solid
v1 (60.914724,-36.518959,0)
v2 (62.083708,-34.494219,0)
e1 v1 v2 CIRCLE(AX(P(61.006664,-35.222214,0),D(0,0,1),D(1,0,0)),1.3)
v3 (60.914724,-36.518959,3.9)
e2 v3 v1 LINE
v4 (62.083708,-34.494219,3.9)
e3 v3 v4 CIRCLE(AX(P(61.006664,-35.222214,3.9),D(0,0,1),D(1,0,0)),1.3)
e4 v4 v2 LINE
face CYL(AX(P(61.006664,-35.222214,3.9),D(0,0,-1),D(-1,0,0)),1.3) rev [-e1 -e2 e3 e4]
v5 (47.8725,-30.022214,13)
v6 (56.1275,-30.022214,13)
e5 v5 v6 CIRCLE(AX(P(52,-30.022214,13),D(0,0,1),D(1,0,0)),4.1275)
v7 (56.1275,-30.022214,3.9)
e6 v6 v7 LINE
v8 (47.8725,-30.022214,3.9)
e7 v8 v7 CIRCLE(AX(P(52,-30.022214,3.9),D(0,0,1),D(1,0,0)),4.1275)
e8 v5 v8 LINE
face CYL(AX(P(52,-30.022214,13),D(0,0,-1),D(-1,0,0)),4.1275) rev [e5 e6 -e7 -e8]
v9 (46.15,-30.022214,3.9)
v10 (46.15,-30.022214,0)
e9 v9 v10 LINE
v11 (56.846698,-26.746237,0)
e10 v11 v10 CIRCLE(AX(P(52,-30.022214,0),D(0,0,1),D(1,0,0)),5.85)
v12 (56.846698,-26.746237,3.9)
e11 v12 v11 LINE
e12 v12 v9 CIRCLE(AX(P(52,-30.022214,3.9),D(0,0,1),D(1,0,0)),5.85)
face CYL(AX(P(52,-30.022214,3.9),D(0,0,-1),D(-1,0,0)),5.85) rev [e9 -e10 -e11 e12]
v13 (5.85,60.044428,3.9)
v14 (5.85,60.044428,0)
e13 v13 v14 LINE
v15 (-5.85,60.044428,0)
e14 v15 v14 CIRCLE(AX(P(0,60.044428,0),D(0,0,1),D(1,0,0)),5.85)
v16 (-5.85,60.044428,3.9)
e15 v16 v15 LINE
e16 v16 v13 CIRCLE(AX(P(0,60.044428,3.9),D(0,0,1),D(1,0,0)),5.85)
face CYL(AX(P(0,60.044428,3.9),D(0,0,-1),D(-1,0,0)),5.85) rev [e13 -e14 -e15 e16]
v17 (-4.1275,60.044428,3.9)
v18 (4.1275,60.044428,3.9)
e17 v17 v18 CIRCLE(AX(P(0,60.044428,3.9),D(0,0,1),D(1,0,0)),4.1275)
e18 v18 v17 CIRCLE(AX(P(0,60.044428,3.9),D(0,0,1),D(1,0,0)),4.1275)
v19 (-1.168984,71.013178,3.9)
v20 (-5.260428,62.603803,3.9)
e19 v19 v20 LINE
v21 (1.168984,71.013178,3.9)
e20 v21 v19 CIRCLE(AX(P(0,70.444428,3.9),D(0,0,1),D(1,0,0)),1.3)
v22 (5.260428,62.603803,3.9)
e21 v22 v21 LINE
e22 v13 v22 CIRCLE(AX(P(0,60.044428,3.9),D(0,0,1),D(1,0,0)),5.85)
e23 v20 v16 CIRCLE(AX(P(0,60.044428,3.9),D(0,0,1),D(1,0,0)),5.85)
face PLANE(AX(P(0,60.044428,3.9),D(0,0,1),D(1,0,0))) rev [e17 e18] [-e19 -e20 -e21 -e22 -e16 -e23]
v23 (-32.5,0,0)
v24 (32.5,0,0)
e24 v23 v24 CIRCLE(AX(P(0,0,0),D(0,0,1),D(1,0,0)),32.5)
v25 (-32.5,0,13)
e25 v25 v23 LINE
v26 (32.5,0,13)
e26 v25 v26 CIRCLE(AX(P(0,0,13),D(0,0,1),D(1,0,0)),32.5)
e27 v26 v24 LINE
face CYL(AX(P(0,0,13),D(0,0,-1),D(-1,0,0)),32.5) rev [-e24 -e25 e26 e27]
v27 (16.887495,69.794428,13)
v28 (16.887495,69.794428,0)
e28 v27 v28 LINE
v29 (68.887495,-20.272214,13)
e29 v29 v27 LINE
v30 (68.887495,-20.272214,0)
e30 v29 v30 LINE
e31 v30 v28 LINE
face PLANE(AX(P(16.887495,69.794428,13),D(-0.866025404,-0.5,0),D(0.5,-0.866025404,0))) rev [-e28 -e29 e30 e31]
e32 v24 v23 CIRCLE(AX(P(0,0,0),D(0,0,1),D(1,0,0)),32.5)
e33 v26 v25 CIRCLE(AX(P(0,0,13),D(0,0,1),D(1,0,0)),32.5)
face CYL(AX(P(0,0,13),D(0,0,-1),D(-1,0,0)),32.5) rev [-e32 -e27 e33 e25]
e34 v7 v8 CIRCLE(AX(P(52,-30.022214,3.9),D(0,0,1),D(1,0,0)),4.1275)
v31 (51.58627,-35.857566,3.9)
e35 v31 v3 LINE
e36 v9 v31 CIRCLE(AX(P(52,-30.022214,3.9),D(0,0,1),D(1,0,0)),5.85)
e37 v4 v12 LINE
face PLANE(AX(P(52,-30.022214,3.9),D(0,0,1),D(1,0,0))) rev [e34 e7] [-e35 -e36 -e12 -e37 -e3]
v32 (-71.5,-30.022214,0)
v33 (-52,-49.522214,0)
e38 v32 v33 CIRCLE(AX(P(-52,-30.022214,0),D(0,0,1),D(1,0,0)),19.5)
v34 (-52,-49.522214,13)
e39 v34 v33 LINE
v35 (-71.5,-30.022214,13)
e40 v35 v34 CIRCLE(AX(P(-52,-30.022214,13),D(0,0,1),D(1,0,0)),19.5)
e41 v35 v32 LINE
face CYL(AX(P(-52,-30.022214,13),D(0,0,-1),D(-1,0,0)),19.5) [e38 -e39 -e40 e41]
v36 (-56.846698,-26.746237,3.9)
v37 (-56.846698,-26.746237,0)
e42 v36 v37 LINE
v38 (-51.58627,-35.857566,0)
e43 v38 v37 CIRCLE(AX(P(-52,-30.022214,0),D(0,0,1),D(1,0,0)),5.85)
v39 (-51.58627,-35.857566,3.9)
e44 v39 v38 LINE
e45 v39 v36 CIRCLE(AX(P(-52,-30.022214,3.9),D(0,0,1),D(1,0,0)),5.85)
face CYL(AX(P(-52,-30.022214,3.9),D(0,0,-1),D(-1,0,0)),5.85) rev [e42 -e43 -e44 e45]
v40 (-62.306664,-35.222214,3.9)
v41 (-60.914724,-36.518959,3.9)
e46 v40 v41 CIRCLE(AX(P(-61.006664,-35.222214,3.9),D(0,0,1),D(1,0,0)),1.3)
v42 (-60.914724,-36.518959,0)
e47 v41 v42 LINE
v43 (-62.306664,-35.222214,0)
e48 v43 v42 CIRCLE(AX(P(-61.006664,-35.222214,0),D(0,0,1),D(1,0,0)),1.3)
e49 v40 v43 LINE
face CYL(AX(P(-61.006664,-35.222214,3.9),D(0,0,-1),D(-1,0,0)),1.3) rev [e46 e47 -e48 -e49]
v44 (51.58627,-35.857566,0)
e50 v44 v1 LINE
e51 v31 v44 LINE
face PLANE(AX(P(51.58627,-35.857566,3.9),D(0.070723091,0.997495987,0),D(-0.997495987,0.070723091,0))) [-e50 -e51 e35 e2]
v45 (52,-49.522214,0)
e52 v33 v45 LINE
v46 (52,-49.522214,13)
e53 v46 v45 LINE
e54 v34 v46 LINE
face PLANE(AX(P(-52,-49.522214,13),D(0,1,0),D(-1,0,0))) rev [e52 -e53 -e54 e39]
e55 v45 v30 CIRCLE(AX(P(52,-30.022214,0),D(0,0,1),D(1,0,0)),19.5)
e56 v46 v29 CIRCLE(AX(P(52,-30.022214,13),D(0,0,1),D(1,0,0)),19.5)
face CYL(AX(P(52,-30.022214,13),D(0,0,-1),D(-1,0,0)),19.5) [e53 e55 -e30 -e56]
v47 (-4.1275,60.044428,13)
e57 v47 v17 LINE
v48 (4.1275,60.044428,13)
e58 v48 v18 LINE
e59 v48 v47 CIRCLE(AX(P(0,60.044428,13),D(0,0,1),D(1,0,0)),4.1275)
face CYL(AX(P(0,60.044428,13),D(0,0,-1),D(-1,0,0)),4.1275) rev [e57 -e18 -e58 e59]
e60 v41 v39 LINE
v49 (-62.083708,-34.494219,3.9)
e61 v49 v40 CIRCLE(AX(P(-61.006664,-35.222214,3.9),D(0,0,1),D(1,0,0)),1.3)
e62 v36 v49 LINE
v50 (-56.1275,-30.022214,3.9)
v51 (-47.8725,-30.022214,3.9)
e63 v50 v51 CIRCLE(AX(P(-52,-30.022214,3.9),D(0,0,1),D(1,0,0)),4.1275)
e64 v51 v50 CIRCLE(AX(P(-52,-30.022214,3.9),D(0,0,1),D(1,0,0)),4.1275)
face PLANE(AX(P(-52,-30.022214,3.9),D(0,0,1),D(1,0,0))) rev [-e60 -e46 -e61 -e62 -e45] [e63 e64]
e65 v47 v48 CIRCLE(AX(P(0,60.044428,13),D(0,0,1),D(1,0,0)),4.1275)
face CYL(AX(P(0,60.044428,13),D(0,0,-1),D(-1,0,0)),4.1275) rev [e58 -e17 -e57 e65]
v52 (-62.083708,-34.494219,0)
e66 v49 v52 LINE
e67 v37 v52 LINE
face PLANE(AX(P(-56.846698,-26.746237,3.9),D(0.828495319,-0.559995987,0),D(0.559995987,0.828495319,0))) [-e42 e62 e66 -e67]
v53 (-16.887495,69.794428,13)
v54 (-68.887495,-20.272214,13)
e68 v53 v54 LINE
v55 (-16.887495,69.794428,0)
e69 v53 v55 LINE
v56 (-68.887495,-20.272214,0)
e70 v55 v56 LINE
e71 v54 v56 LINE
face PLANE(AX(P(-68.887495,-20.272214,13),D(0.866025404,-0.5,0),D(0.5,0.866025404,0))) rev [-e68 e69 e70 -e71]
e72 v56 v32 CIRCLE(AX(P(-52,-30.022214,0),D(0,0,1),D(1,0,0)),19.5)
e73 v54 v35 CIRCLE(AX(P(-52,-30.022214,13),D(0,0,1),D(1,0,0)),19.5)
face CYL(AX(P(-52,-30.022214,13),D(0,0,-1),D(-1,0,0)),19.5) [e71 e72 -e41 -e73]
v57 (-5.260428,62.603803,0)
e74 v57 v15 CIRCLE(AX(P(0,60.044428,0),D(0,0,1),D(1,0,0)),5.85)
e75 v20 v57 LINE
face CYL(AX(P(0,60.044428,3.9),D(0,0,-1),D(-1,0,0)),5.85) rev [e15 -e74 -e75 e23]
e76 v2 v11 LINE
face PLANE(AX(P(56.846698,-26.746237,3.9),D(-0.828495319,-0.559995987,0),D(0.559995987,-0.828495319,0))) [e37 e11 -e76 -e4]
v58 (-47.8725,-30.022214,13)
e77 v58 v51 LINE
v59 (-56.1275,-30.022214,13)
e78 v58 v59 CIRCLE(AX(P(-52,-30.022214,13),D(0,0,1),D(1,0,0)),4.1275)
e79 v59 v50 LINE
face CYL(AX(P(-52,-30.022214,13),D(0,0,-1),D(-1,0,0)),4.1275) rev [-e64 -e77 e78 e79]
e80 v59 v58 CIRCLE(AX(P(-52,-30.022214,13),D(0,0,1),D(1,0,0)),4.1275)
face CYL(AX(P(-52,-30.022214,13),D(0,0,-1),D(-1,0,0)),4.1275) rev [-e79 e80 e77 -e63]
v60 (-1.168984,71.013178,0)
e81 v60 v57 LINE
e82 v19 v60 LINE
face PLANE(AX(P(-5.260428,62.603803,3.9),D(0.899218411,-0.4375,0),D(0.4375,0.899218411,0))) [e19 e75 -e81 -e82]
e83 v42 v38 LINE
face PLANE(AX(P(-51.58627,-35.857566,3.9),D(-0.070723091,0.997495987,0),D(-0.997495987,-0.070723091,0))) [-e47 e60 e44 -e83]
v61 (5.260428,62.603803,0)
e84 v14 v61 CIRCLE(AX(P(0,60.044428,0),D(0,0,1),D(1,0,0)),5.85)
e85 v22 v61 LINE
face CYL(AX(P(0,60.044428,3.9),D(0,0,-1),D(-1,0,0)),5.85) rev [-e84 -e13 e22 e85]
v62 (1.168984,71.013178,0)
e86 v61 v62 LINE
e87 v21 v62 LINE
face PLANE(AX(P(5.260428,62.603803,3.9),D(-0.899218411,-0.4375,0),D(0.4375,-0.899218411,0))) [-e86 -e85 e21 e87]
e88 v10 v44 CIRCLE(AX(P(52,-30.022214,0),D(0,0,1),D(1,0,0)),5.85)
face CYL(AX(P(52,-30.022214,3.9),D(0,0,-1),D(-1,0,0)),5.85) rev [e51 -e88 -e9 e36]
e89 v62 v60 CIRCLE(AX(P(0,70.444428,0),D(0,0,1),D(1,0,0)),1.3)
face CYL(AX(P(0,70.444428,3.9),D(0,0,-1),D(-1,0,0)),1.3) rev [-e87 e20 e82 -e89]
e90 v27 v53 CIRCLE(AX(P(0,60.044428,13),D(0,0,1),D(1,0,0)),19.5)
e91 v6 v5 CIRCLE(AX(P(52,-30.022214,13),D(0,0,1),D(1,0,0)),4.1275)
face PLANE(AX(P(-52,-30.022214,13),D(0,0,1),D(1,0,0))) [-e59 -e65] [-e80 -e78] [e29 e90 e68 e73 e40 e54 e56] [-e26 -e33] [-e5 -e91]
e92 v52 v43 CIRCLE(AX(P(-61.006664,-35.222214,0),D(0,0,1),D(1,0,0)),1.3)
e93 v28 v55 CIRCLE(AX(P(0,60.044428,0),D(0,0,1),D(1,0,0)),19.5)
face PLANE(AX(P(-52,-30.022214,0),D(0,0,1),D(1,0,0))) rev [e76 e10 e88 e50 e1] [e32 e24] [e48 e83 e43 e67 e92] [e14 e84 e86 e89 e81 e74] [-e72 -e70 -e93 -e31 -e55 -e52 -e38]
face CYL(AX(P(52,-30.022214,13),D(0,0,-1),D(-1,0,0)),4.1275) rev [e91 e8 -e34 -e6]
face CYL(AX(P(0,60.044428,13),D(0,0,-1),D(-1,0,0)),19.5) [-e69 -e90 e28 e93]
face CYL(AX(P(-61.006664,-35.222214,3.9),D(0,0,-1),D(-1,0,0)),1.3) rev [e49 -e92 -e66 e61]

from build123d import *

# Parameters (mm, degrees)
SKETCH1_R           = 3.175
SKETCH1_R_2         = 25
BOSS_EXTRUDE1_DEPTH = 10
SKETCH2_R           = 3.175
CUT_EXTRUDE1_DEPTH  = 3
SCALE_RATIO_1_SCALE = 1.3


with BuildPart() as part:
    # Sketch1 → Boss-Extrude1 (new body)
    with BuildSketch(Plane.XY):
        with BuildLine():
            Line((-52.990381057, -15.594010768), (-12.990381057, 53.688021535))
            ThreePointArc((-12.990381057, 53.688021535), (0, 61.188021535), (12.990381057, 53.688021535))
            Line((12.990381057, 53.688021535), (52.990381057, -15.594010768))
            ThreePointArc((52.990381057, -15.594010768), (52.990381057, -30.594010768), (40, -38.094010768))
            Line((40, -38.094010768), (-40, -38.094010768))
            ThreePointArc((-40, -38.094010768), (-52.990381057, -30.594010768), (-52.990381057, -15.594010768))
        make_face()
        with Locations((-40, -23.094010768)):
            Circle(SKETCH1_R, mode=Mode.SUBTRACT)
        with Locations((40, -23.094010768)):
            Circle(SKETCH1_R, mode=Mode.SUBTRACT)
        with Locations((0, 46.188021535)):
            Circle(SKETCH1_R, mode=Mode.SUBTRACT)
        Circle(SKETCH1_R_2, mode=Mode.SUBTRACT)
    extrude(amount=BOSS_EXTRUDE1_DEPTH)

    # Sketch2 → Cut-Extrude1 (cut)
    # profile 1 of 3: a face of its own
    with BuildSketch(Plane.XY):
        with BuildLine():
            Line((-39.68174609, -27.58274271), (-46.857480139, -28.091506755))
            ThreePointArc((-46.857480139, -28.091506755), (-47.794228634, -27.594010768), (-47.75669855, -26.53401478))
            Line((-47.75669855, -26.53401478), (-43.728228938, -20.574028825))
            ThreePointArc((-43.728228938, -20.574028825), (-36.102885683, -20.844010768), (-39.68174609, -27.58274271))
        make_face()
        with Locations((-40, -23.094010768)):
            Circle(SKETCH2_R, mode=Mode.SUBTRACT)
    # profile 2 of 3: a face of its own
    with BuildSketch(Plane.XY):
        with BuildLine():
            Line((-4.046482848, 48.156771535), (-0.899218411, 54.625521535))
            ThreePointArc((-0.899218411, 54.625521535), (0, 55.188021535), (0.899218411, 54.625521535))
            Line((0.899218411, 54.625521535), (4.046482848, 48.156771535))
            ThreePointArc((4.046482848, 48.156771535), (0, 41.688021535), (-4.046482848, 48.156771535))
        make_face()
        with Locations((0, 46.188021535)):
            Circle(SKETCH2_R, mode=Mode.SUBTRACT)
    # profile 3 of 3: a face of its own
    with BuildSketch(Plane.XY):
        with BuildLine():
            Line((43.728228938, -20.574028825), (47.75669855, -26.53401478))
            ThreePointArc((47.75669855, -26.53401478), (47.794228634, -27.594010768), (46.857480139, -28.091506755))
            Line((46.857480139, -28.091506755), (39.68174609, -27.58274271))
            ThreePointArc((39.68174609, -27.58274271), (36.102885683, -20.844010768), (43.728228938, -20.574028825))
        make_face()
        with Locations((40, -23.094010768)):
            Circle(SKETCH2_R, mode=Mode.SUBTRACT)
    extrude(amount=CUT_EXTRUDE1_DEPTH, mode=Mode.SUBTRACT)


with BuildPart() as part_1:
    # Scale ratio 1: scaled about (0, 0, 0)
    add(part.part.scale(SCALE_RATIO_1_SCALE))


solid = part_1.part
